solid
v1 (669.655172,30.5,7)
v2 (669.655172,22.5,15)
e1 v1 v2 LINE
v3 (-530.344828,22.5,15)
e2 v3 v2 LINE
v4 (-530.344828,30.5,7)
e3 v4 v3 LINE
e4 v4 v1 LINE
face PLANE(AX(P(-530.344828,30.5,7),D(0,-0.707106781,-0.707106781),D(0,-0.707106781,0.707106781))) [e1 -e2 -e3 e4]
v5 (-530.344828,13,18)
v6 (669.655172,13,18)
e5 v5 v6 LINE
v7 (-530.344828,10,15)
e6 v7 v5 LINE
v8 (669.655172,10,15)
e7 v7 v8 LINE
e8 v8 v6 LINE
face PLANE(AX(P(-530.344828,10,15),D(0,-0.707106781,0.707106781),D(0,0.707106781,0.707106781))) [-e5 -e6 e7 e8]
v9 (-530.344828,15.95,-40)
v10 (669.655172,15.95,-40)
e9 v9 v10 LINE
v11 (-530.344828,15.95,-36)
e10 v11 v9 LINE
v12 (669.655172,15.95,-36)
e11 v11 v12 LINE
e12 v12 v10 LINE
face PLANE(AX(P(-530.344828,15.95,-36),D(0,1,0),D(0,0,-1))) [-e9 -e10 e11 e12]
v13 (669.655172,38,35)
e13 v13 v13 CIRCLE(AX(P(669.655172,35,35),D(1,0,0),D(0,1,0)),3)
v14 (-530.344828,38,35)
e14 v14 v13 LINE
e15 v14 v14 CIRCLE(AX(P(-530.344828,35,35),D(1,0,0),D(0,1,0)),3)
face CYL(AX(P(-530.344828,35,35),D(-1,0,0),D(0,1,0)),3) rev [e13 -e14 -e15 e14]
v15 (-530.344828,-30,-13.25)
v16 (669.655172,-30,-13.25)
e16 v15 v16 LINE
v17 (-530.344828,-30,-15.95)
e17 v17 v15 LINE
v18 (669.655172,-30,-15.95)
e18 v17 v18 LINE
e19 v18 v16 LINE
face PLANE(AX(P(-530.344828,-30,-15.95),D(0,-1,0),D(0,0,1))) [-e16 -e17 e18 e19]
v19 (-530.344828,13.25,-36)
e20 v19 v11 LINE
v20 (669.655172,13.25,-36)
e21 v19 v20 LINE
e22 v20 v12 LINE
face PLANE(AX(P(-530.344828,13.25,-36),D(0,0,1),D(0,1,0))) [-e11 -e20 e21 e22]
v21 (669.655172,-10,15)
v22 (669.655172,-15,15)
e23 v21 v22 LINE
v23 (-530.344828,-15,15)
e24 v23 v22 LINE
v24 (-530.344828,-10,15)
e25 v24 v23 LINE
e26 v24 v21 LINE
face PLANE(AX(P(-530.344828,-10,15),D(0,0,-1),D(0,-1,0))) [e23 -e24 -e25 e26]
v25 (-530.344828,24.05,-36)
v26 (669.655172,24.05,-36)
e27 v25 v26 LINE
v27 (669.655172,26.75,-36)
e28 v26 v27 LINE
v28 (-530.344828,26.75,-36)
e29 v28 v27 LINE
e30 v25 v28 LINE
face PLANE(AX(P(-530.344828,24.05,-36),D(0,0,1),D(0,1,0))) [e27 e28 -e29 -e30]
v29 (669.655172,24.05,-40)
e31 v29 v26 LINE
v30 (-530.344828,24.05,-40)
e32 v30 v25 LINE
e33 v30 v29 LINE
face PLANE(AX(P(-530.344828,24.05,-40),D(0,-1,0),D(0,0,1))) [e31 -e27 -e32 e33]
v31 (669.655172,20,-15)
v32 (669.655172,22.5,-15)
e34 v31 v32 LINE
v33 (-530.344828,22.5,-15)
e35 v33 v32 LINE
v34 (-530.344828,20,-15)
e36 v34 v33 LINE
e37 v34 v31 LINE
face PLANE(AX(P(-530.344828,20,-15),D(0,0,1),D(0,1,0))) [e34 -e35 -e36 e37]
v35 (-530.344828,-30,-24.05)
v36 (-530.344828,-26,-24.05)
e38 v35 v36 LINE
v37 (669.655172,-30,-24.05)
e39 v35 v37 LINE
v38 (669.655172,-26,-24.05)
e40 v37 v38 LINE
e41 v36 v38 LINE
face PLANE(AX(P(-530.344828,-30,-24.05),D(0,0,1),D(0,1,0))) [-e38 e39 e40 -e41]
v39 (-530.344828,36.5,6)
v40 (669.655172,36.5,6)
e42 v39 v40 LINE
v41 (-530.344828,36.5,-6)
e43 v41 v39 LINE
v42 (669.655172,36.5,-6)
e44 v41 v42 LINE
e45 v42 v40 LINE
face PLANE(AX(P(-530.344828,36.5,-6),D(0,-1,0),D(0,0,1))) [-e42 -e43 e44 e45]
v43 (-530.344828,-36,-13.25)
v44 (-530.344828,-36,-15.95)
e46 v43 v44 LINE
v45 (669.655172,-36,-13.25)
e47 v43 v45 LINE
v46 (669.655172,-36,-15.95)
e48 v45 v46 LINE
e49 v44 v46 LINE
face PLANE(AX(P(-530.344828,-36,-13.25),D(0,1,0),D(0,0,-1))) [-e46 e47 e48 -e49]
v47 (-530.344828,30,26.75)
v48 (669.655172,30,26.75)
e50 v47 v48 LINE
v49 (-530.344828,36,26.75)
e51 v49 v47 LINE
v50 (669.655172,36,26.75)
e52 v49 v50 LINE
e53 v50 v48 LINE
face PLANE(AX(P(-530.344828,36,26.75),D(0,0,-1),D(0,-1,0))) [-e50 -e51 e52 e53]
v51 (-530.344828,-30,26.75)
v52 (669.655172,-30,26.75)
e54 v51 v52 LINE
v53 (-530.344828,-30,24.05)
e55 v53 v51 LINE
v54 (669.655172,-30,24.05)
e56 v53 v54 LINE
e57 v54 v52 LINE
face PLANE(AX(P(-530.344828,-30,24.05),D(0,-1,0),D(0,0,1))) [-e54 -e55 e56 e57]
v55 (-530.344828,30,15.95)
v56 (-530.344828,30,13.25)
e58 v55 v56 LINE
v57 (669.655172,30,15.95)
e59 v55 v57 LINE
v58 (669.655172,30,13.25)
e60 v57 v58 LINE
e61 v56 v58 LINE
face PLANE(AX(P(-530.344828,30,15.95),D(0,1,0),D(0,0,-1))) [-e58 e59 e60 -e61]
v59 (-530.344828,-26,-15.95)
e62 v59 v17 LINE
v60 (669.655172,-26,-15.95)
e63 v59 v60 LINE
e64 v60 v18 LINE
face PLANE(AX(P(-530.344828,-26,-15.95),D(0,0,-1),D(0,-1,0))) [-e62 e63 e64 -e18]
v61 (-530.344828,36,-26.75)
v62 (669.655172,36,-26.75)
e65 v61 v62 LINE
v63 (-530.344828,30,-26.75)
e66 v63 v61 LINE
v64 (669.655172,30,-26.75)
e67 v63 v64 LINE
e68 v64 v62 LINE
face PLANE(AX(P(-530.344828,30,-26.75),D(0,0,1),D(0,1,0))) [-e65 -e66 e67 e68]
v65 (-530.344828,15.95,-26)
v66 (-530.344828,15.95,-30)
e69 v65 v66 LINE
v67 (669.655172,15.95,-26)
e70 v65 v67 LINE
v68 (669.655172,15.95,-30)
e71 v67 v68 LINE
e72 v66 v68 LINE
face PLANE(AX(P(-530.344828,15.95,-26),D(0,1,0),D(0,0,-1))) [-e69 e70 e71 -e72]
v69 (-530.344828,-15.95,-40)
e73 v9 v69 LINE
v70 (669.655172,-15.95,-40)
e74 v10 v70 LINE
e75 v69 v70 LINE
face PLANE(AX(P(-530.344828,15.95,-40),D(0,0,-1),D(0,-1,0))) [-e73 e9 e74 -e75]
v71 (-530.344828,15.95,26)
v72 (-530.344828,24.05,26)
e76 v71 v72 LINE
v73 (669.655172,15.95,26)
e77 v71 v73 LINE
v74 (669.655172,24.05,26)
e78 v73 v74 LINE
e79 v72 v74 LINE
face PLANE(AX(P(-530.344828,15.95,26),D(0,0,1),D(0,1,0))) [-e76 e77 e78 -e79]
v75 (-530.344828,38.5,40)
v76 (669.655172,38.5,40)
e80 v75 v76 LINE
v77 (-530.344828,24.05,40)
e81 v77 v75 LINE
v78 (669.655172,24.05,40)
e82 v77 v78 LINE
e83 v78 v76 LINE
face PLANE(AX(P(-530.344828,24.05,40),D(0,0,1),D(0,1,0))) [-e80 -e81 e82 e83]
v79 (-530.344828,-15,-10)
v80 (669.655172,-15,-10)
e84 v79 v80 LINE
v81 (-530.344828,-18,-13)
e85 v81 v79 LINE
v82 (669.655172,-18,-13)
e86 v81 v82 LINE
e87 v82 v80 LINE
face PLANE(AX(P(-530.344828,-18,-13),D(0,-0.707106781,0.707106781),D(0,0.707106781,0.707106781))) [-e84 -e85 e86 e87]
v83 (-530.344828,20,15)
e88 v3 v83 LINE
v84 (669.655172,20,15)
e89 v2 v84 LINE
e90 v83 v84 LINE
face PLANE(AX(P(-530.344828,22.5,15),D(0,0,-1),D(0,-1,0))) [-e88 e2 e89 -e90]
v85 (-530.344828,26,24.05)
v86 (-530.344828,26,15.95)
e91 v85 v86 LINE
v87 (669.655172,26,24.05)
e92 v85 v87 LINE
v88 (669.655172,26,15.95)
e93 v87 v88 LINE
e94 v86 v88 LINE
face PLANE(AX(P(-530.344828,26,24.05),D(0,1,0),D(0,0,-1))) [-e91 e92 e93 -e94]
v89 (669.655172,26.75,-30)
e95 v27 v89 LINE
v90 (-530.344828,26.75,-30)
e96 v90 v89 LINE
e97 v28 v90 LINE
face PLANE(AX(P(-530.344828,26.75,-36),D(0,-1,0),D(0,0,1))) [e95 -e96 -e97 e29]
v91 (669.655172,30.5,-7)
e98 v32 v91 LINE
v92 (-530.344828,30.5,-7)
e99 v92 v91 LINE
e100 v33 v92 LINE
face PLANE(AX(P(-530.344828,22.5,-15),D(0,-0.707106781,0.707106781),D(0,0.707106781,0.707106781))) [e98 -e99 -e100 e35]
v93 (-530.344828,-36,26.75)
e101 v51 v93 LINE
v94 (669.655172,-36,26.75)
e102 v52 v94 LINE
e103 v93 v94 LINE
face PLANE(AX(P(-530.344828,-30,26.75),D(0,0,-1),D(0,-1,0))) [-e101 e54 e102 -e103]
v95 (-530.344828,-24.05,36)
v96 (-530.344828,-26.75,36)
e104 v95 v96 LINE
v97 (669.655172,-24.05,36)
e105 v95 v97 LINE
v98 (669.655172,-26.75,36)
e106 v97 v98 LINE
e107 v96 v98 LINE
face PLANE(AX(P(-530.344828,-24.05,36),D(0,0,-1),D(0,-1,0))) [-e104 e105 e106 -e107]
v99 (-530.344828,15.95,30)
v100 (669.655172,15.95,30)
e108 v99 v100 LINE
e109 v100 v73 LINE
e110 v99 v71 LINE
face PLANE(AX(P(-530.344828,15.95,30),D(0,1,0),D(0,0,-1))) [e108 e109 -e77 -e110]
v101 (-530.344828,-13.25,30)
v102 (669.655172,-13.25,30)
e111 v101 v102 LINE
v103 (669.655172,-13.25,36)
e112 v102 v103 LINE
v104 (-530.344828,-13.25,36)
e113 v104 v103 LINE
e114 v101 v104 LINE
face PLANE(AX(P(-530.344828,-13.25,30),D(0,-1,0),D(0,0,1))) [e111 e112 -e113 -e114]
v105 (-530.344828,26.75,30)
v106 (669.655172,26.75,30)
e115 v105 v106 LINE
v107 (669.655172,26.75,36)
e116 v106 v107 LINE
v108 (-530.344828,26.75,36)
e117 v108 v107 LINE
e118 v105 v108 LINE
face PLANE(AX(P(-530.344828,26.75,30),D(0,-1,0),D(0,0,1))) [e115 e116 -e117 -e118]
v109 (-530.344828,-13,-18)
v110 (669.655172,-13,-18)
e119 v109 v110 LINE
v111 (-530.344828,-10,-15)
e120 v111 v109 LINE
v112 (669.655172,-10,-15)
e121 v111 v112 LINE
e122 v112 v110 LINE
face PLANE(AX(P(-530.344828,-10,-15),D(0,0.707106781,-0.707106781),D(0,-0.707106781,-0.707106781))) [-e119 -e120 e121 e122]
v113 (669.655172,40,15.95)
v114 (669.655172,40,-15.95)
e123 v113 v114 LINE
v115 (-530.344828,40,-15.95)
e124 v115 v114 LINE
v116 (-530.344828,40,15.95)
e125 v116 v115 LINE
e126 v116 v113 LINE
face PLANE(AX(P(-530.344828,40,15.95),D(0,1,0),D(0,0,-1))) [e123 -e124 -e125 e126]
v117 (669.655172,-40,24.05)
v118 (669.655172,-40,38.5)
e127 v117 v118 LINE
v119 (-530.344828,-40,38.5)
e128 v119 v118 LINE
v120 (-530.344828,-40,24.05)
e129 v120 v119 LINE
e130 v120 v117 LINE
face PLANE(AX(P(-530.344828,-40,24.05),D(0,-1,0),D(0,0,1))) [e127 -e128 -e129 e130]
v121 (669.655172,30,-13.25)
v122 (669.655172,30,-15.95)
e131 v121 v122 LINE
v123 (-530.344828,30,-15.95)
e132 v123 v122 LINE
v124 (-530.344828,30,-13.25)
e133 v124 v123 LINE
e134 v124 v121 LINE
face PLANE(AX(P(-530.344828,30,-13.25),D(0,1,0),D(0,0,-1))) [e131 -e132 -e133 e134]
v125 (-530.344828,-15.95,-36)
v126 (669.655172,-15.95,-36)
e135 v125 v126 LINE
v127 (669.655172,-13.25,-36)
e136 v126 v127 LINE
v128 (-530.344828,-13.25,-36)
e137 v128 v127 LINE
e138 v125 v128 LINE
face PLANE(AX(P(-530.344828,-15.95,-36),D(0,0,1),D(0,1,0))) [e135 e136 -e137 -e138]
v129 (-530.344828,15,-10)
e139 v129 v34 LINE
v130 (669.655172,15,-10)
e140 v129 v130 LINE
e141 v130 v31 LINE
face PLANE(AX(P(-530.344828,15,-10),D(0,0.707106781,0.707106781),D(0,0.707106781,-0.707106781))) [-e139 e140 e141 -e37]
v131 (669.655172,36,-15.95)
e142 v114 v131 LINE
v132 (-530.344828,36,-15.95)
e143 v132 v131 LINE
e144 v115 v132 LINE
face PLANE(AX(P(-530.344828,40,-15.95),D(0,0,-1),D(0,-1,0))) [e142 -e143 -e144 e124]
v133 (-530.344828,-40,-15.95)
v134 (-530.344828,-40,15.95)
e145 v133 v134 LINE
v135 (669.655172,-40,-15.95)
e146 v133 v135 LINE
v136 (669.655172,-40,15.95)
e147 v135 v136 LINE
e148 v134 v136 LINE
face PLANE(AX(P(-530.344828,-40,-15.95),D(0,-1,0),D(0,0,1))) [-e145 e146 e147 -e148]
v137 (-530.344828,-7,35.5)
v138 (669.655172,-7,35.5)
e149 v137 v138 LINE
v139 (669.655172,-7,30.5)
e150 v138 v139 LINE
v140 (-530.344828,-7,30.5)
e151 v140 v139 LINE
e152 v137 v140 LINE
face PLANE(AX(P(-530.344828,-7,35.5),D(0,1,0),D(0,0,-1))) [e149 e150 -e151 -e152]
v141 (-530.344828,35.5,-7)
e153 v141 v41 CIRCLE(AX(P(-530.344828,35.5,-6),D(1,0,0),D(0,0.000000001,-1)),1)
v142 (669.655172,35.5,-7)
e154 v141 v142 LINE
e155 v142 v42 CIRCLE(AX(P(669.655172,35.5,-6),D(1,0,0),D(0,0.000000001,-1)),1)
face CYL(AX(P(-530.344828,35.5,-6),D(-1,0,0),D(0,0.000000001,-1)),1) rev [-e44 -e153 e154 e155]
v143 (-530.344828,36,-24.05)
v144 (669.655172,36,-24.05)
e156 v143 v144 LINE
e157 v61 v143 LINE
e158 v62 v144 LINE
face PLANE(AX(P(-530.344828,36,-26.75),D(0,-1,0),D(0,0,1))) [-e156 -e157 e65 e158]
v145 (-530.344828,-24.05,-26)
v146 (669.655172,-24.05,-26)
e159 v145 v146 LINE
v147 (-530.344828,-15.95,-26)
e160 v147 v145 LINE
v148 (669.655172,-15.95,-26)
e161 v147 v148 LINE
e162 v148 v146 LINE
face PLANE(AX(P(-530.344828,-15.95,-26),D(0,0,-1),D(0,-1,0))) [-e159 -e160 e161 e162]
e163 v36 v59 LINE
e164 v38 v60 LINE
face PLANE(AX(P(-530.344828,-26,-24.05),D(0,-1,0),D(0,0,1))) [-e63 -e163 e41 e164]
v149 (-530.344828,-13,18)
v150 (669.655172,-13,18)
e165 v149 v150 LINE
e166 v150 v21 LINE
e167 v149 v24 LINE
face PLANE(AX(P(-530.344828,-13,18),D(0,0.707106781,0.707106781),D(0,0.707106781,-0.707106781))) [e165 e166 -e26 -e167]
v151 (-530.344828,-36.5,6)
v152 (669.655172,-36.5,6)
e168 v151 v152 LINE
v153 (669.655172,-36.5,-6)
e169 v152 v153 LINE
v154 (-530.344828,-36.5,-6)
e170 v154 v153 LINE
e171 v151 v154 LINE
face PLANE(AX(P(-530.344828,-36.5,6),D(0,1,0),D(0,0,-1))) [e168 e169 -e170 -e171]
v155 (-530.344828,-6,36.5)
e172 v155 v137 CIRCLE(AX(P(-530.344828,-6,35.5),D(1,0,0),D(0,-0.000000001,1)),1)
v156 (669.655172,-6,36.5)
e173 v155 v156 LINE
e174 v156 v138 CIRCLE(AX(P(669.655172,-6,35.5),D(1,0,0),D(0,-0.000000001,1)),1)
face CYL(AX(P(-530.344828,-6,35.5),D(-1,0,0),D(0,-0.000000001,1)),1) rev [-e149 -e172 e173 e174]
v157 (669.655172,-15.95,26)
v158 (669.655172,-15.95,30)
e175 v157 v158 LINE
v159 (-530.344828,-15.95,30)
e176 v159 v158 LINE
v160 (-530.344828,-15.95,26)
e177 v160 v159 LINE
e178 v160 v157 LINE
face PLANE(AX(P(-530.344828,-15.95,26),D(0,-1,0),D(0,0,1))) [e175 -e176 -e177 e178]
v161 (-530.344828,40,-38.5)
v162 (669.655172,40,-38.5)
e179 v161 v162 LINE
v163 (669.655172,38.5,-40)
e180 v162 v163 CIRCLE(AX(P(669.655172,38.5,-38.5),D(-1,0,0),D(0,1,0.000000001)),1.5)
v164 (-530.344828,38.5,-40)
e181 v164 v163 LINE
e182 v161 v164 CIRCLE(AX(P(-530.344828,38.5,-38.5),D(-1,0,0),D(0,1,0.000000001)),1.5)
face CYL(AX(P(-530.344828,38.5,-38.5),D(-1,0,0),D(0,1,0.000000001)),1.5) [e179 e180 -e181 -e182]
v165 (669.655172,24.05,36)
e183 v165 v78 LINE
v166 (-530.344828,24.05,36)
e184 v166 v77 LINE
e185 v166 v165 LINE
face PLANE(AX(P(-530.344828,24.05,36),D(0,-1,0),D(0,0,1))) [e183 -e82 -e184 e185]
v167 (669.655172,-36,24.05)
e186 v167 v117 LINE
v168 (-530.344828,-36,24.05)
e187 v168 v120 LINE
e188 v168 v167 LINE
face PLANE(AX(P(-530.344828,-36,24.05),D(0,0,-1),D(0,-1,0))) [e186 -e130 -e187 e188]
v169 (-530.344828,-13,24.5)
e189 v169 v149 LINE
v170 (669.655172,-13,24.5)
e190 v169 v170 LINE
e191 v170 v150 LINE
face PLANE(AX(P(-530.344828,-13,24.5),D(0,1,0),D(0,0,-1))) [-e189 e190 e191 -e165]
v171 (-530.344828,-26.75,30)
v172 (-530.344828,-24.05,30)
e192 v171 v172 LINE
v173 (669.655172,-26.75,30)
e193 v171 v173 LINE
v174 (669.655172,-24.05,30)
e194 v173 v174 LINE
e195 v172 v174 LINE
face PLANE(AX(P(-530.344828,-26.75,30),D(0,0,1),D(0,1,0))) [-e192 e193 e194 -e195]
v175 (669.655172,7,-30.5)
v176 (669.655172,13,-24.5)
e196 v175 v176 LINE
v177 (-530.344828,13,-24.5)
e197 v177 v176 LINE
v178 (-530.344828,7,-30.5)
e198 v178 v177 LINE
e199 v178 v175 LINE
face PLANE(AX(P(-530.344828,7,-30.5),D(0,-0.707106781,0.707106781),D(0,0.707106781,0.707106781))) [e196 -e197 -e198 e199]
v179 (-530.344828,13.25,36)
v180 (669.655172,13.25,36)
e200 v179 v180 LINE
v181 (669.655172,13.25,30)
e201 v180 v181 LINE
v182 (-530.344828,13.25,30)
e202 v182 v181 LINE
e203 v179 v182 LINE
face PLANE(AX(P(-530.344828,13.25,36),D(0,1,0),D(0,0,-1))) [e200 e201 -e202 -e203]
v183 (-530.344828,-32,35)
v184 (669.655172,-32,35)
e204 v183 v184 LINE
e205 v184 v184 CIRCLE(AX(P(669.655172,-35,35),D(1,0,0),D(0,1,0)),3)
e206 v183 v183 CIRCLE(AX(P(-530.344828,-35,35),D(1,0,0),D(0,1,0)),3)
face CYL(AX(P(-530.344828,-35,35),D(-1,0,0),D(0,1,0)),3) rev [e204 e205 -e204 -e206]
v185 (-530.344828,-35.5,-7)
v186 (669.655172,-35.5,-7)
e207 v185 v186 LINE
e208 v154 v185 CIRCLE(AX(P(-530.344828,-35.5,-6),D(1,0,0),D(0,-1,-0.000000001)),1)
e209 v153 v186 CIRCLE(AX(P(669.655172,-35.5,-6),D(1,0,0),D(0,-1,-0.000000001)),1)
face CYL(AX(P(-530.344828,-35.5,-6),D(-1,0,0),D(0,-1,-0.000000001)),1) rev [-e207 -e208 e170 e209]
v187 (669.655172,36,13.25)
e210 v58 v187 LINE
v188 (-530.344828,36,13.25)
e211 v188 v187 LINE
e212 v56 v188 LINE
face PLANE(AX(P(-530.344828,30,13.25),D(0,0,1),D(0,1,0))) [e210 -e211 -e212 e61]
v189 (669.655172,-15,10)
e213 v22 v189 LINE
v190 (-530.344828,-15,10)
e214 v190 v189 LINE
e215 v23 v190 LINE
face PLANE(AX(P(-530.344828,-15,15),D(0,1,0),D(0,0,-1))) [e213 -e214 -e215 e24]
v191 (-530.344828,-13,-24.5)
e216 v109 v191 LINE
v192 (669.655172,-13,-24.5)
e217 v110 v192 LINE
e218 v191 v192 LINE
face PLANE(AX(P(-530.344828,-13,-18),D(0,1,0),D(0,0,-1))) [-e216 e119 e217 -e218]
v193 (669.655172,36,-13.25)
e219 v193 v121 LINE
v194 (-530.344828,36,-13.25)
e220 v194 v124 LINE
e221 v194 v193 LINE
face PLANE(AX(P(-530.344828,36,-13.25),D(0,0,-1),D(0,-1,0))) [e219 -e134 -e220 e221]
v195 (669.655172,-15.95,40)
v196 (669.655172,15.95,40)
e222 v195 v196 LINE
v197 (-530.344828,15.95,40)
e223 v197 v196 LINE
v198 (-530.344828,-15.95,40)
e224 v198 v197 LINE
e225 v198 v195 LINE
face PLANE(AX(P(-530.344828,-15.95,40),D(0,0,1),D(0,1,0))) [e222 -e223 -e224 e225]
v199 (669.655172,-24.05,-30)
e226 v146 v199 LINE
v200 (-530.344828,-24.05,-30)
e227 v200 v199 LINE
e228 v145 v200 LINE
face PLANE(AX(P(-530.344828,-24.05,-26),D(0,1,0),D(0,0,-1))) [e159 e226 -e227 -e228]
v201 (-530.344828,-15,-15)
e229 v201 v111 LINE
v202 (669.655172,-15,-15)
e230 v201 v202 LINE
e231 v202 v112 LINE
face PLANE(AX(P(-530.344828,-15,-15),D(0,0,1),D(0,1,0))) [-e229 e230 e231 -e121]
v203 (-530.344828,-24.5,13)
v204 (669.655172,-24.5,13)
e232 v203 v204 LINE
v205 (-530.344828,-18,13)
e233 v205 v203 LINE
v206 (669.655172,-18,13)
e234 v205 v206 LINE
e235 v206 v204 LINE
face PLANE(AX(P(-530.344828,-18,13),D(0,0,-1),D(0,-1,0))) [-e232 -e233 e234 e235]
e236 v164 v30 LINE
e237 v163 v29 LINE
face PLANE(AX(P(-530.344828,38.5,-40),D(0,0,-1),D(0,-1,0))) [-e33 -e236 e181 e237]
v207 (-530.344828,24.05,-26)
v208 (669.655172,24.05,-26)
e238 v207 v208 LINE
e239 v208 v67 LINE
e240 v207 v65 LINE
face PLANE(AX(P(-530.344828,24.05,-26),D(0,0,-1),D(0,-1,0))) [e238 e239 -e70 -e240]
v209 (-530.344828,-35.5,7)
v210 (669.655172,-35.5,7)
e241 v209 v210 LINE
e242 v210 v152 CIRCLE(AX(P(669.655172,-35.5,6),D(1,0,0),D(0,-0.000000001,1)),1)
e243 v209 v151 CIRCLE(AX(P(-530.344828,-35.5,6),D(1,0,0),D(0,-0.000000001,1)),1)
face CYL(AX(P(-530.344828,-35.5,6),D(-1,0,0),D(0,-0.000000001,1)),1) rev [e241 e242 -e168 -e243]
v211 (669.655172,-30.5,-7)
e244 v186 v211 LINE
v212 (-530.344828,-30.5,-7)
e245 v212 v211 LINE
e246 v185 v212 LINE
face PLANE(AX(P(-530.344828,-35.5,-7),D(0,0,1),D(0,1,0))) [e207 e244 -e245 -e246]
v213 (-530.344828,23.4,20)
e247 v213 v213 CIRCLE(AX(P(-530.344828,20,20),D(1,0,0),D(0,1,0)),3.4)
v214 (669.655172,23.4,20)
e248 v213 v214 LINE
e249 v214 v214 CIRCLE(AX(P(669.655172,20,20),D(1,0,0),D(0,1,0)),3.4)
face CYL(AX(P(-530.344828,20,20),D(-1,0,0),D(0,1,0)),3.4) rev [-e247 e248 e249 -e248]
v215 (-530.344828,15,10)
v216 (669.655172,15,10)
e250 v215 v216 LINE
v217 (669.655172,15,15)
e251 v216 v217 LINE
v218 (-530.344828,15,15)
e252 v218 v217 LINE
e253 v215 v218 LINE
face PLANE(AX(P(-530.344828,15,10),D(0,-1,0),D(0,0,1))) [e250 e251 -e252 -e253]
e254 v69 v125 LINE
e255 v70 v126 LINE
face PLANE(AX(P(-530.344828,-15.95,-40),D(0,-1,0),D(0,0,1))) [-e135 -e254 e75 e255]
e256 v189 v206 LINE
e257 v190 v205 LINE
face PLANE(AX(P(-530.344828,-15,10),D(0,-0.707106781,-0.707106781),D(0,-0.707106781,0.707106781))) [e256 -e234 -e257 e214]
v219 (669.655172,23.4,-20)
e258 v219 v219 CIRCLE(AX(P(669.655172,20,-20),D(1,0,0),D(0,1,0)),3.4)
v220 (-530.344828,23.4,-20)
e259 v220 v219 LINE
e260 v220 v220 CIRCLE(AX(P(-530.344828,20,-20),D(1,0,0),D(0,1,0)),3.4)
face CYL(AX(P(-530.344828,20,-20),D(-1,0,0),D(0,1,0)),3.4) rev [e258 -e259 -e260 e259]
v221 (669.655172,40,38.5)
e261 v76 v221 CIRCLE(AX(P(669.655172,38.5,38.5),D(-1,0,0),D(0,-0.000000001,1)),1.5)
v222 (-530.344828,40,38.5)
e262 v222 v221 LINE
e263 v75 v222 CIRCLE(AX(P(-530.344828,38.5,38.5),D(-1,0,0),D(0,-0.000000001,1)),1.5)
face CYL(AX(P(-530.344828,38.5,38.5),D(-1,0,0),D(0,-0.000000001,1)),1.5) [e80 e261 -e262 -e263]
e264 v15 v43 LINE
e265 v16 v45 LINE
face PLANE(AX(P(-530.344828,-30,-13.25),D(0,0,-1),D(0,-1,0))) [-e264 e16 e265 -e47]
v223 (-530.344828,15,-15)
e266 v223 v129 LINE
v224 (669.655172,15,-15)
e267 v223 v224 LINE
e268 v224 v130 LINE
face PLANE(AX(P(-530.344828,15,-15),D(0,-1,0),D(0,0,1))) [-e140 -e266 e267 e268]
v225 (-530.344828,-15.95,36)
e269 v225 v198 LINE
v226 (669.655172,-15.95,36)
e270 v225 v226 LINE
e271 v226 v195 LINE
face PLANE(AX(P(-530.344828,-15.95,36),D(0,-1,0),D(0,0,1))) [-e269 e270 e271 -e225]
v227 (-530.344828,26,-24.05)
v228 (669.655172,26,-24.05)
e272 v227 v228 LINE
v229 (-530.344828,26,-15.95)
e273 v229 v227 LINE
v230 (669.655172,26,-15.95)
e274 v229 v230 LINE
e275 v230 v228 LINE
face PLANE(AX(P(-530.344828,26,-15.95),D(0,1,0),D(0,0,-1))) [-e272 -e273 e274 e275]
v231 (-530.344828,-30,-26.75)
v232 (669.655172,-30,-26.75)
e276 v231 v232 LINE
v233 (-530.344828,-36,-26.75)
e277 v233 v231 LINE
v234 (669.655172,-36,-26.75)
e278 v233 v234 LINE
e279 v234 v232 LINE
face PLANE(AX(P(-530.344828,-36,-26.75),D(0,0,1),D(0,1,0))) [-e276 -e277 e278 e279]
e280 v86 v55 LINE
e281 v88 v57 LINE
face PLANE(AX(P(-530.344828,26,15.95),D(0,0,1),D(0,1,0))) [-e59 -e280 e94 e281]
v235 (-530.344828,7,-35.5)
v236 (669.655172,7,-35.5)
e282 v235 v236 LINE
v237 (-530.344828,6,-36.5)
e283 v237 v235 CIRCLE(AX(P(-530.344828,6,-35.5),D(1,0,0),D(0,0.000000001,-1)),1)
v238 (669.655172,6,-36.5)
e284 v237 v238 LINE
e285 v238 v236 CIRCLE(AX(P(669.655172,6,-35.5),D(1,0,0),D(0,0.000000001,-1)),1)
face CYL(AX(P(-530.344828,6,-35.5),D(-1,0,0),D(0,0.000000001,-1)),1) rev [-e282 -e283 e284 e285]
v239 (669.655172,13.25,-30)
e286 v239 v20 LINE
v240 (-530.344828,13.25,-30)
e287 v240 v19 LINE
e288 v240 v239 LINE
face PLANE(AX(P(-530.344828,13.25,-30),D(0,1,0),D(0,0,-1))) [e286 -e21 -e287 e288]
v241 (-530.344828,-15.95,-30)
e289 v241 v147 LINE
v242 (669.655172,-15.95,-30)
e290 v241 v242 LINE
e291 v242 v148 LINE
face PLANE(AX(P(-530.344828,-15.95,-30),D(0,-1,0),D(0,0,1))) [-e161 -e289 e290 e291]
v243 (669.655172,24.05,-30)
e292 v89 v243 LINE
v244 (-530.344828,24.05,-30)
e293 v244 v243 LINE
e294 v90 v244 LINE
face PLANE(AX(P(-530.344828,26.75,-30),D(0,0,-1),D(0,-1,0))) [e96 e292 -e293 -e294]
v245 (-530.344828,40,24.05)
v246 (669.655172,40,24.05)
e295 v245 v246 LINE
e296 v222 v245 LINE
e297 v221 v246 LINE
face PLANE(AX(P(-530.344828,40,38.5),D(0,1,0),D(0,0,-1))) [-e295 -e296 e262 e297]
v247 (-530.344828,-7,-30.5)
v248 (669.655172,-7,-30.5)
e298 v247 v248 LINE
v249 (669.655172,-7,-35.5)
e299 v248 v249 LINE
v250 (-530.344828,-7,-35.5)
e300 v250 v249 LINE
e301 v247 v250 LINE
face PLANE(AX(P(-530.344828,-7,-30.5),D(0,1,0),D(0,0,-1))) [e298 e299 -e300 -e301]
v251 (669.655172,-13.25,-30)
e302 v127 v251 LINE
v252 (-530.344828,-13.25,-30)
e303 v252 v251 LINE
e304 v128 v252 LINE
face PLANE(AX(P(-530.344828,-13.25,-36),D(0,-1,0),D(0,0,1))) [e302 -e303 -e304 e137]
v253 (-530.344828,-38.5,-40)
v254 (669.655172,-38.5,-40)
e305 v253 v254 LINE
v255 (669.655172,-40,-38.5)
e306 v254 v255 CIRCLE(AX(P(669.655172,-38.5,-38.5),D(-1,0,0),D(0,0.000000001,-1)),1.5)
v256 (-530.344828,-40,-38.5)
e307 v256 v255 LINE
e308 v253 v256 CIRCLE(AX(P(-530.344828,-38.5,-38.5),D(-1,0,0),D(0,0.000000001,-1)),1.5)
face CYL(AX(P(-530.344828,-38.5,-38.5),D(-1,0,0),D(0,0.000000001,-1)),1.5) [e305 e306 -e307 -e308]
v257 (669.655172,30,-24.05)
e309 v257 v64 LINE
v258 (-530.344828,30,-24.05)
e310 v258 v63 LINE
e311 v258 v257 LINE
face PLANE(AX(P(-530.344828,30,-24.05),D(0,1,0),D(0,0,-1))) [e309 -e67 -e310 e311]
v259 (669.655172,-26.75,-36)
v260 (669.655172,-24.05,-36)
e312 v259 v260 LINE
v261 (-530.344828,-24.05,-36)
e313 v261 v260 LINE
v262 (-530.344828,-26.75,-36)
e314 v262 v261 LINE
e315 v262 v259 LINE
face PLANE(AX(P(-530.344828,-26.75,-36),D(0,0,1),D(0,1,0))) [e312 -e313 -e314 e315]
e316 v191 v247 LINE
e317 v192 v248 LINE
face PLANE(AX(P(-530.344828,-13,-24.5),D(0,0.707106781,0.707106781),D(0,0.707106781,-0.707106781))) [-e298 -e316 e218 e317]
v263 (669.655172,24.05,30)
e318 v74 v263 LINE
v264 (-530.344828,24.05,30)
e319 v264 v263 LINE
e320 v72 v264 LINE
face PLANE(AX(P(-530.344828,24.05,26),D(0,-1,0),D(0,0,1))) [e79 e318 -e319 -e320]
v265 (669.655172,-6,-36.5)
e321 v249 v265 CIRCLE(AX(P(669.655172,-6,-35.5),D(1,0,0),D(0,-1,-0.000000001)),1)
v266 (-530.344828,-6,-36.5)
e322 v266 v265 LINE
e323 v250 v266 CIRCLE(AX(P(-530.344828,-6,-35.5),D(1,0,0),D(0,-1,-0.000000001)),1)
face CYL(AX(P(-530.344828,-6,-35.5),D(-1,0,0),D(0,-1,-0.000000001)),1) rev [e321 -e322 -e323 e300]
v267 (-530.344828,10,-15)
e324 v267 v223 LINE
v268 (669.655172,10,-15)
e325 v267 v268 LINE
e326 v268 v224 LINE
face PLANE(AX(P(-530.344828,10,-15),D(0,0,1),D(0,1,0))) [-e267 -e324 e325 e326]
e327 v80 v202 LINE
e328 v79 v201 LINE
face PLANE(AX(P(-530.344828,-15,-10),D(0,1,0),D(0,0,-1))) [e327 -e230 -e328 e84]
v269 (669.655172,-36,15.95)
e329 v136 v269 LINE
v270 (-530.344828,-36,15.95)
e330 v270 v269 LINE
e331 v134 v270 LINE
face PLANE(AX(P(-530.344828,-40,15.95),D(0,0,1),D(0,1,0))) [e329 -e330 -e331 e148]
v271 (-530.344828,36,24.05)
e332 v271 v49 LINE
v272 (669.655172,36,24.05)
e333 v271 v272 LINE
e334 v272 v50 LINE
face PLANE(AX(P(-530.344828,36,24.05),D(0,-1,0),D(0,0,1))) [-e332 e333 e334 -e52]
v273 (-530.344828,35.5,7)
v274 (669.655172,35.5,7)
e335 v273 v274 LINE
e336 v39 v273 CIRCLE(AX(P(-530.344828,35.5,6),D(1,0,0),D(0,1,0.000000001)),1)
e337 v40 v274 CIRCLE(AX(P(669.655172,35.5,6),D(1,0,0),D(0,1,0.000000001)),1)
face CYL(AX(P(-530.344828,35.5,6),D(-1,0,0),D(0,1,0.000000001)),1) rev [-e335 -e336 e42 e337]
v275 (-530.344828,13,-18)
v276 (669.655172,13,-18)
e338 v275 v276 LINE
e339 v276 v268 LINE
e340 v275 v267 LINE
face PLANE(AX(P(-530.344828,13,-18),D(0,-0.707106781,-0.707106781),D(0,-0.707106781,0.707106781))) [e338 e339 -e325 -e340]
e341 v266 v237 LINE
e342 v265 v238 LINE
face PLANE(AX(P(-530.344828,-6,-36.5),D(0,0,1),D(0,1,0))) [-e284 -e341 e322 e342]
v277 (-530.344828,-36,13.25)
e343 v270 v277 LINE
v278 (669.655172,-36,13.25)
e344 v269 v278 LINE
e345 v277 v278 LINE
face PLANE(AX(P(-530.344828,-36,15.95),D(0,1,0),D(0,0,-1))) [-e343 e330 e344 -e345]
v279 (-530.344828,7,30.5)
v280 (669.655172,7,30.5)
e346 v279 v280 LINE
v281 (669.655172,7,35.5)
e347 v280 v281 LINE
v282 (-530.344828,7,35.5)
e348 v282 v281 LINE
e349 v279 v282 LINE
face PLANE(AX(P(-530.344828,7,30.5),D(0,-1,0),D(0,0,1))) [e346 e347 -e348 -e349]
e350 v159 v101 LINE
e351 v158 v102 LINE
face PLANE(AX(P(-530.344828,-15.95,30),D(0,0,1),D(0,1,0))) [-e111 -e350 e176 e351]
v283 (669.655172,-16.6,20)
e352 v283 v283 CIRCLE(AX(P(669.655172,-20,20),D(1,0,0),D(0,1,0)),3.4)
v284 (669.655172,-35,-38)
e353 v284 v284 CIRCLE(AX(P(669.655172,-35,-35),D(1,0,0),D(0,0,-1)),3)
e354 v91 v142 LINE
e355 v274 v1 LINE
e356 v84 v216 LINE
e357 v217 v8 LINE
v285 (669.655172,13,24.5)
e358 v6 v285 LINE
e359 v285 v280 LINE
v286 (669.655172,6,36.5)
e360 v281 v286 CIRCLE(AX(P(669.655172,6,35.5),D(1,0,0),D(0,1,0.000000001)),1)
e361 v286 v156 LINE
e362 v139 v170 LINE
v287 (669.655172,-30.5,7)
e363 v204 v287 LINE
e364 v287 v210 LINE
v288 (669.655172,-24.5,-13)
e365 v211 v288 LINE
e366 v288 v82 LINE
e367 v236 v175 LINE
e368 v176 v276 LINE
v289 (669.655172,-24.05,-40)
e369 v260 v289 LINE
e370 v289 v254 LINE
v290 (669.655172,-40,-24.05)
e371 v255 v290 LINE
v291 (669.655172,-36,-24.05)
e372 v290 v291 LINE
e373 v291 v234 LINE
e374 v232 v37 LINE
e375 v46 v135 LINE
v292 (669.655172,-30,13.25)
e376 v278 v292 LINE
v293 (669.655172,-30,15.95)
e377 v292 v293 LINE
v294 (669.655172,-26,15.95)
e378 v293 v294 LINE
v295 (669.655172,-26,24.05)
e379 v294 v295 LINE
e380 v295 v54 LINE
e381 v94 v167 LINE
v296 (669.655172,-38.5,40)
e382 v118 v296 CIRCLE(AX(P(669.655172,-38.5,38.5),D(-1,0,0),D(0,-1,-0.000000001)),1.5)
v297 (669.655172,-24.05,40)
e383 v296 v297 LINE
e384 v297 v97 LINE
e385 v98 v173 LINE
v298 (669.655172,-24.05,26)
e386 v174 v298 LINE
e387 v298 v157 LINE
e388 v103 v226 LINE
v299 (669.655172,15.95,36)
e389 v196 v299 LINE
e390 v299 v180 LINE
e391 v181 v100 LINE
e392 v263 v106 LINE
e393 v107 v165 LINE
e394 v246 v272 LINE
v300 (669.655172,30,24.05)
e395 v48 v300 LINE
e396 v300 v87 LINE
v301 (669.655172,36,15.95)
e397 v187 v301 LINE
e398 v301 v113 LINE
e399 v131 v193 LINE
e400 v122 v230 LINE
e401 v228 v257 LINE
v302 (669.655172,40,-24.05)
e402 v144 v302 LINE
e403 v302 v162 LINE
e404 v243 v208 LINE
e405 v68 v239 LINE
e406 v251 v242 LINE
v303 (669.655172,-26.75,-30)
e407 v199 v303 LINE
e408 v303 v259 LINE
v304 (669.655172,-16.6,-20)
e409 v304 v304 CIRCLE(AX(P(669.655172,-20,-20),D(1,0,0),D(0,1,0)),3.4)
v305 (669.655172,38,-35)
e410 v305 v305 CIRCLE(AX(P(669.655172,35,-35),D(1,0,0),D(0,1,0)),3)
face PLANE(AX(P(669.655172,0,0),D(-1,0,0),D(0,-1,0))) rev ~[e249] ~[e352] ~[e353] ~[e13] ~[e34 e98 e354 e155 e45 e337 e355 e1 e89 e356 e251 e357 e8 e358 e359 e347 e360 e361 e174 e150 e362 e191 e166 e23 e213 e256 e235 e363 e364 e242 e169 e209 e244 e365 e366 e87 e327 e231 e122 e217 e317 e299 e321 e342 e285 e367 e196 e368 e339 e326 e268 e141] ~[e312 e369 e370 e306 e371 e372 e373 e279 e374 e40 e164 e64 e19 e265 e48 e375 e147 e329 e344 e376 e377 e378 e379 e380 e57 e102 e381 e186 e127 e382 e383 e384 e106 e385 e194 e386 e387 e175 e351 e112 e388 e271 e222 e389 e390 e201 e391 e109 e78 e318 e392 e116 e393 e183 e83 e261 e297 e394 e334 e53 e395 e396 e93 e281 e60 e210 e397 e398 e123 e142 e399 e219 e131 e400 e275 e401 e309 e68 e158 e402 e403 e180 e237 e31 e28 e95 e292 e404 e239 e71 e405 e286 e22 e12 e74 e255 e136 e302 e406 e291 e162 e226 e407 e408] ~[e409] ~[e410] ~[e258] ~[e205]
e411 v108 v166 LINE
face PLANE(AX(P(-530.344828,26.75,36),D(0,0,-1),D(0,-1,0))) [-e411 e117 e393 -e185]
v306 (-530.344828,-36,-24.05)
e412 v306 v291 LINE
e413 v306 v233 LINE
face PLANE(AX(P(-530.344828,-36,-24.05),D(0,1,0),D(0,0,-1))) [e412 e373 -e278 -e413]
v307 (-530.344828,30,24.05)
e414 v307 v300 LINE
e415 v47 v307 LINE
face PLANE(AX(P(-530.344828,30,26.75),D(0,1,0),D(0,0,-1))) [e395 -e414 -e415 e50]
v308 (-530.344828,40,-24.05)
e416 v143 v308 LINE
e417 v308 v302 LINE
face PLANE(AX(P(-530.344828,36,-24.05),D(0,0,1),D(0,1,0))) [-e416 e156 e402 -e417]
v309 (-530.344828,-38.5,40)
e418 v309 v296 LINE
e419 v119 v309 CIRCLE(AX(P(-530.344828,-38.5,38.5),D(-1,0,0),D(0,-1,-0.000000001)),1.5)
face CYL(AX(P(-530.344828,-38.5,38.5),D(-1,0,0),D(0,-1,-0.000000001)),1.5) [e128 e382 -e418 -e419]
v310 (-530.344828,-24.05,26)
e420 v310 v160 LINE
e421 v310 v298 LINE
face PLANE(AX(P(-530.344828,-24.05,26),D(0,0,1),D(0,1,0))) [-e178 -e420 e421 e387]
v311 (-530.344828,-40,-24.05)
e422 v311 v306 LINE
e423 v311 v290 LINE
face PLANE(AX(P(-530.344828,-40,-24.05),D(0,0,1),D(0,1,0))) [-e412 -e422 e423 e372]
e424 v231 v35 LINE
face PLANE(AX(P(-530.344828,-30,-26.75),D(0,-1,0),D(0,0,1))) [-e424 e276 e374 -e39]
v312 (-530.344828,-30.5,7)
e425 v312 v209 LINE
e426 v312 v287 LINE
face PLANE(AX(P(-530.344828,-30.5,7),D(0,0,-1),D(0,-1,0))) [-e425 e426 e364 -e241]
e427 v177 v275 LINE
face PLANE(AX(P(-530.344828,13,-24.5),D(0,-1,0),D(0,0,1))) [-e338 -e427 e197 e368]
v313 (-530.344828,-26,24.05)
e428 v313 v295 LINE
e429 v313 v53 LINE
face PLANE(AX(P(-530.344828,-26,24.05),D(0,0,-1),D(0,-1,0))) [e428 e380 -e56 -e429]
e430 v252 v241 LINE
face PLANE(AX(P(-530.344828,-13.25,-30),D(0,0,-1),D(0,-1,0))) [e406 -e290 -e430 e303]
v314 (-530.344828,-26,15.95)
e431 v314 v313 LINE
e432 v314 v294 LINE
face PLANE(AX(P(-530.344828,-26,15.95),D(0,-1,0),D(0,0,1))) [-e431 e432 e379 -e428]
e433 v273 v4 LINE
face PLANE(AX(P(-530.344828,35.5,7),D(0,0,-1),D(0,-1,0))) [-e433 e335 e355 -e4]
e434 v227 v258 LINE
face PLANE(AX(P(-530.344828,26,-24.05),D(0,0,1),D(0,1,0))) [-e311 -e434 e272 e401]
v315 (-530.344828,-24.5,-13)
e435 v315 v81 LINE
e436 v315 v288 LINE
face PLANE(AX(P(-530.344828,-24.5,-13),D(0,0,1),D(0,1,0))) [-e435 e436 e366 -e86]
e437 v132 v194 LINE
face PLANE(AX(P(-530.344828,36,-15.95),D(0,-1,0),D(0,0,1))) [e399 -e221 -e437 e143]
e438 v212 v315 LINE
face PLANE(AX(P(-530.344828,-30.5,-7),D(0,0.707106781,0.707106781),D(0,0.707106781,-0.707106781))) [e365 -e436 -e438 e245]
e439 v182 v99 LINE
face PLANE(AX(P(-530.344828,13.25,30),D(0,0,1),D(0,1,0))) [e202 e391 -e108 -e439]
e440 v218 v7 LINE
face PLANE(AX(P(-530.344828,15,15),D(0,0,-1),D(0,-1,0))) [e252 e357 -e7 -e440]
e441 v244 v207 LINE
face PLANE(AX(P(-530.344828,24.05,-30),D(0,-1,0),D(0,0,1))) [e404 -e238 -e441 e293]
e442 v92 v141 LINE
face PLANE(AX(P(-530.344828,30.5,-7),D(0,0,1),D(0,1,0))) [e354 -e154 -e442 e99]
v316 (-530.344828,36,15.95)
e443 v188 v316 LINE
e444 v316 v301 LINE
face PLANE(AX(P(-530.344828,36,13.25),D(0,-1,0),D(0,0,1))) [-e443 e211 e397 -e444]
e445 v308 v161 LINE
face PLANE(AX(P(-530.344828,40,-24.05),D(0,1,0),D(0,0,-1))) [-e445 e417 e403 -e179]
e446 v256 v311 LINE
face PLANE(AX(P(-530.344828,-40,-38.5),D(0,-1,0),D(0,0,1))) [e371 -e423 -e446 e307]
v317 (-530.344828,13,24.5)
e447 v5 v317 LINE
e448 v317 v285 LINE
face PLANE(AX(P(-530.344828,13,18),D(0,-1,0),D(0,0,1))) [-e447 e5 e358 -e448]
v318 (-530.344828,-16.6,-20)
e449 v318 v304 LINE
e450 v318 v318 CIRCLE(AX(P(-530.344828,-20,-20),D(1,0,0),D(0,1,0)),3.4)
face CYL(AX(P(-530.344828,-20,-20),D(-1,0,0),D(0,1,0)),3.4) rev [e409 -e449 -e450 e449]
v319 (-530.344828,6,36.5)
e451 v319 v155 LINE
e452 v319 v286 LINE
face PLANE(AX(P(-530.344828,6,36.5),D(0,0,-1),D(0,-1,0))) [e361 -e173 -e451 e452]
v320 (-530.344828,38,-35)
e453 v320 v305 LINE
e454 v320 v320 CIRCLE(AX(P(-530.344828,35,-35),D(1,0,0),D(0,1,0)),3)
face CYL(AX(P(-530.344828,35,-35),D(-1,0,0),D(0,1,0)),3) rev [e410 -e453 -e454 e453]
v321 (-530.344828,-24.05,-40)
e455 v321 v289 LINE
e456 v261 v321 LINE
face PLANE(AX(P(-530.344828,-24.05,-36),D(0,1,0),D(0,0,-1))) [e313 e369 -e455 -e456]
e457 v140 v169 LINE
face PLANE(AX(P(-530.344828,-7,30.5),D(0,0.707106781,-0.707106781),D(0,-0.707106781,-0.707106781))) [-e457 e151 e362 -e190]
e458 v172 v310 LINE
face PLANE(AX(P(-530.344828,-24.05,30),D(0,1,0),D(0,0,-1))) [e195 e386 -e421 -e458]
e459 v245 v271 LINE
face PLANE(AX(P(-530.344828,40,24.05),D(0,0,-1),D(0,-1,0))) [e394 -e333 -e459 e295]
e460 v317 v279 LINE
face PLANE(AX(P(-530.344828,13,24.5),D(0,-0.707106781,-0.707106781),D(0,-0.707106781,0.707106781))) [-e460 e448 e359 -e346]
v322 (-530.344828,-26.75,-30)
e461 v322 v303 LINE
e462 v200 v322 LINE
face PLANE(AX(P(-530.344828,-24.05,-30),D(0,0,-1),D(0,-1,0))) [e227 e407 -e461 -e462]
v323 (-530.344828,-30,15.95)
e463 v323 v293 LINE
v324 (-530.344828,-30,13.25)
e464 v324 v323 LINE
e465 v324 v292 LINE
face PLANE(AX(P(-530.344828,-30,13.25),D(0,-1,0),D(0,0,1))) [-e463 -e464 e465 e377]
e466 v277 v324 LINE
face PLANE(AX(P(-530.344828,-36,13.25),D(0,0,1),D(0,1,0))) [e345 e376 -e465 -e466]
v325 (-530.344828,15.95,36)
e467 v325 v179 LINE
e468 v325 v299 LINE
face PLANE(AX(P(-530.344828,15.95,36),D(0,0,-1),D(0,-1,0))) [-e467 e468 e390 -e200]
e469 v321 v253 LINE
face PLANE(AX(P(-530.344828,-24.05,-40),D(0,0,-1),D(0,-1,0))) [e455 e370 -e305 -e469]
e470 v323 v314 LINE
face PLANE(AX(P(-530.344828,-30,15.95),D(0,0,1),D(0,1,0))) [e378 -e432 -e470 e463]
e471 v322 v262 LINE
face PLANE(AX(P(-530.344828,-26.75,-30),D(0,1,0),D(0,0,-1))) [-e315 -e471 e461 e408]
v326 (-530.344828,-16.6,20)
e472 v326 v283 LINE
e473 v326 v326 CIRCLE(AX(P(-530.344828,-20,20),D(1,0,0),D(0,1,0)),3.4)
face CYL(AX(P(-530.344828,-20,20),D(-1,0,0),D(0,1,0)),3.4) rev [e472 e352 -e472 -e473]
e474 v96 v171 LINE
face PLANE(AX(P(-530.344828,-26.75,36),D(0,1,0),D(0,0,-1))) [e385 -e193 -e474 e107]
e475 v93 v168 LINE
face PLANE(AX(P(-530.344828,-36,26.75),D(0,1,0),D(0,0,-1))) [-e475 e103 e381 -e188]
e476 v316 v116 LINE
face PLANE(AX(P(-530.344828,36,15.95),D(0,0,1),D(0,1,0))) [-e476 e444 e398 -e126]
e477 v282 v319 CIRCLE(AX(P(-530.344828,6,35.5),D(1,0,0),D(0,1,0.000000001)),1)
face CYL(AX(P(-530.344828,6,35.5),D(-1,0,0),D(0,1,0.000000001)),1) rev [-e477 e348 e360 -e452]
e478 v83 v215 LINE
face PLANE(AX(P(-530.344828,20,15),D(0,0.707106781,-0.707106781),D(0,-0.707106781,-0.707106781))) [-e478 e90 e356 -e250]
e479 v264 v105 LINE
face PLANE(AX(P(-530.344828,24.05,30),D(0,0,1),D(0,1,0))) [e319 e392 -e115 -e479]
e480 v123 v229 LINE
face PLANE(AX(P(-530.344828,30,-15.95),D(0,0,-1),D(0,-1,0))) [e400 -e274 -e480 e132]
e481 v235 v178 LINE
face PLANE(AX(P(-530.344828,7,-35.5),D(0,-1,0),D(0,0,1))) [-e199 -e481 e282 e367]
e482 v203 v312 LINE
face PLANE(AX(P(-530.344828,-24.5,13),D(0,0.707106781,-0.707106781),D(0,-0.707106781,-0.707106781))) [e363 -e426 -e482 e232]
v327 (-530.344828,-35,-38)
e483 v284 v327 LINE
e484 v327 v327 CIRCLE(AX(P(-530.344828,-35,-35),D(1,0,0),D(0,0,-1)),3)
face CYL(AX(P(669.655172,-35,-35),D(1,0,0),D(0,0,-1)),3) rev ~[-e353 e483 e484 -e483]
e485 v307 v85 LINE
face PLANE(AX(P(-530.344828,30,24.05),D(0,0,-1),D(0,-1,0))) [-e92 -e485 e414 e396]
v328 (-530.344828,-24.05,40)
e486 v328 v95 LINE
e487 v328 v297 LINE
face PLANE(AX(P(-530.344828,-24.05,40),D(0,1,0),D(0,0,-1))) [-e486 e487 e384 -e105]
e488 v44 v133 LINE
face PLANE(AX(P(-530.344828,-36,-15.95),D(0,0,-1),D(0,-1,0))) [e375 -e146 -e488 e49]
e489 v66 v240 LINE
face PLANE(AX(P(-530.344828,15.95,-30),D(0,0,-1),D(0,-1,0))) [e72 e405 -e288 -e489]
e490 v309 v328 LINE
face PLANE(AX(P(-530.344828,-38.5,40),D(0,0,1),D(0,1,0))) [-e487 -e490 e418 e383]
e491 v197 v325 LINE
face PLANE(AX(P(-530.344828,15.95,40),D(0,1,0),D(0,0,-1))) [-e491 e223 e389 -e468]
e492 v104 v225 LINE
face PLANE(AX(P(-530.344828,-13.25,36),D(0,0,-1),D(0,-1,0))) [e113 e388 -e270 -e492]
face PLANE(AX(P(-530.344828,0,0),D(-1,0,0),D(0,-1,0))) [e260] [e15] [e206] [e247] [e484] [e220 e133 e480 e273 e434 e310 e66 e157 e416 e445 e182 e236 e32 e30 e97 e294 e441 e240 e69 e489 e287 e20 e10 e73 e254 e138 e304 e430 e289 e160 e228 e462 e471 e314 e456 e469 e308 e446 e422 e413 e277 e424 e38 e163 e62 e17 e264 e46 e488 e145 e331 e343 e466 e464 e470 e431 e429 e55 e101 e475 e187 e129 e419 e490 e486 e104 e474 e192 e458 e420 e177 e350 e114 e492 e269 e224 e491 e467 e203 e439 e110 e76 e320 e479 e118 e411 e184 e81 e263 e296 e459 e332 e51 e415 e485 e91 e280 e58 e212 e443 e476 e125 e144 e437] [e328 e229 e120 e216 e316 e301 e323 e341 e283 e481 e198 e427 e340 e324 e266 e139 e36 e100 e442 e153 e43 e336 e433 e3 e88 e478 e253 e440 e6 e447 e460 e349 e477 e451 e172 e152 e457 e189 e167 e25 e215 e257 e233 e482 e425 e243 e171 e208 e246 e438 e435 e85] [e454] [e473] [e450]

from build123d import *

# Parameters (mm, degrees)
SKETCH1_R                                = 3.4
SKETCH1_R_2                              = 3
ALUMINUM_PROFILE_80_X_80G_X_R1_5_1_DEPTH = 1200
SKETCH10_R                               = 3
CUT_EXTRUDE1_DEPTH                       = 1202.332593414


with BuildPart() as part:
    # Sketch1 → Aluminum profile 80 X 80G X R1.5(1) (new body)
    with BuildSketch(Plane.YZ.offset(-530.344827586)):
        with BuildLine():
            Line((-24.05, 40), (-24.05, 36))
            Line((-24.05, 36), (-26.75, 36))
            Line((-26.75, 36), (-26.75, 30))
            Line((-26.75, 30), (-24.05, 30))
            Line((-24.05, 30), (-24.05, 26))
            Line((-24.05, 26), (-15.95, 26))
            Line((-15.95, 26), (-15.95, 30))
            Line((-15.95, 30), (-13.25, 30))
            Line((-13.25, 30), (-13.25, 36))
            Line((-13.25, 36), (-15.95, 36))
            Line((-15.95, 36), (-15.95, 40))
            Line((-15.95, 40), (15.95, 40))
            Line((15.95, 40), (15.95, 36))
            Line((15.95, 36), (13.25, 36))
            Line((13.25, 36), (13.25, 30))
            Line((13.25, 30), (15.95, 30))
            Line((15.95, 30), (15.95, 26))
            Line((15.95, 26), (24.05, 26))
            Line((24.05, 26), (24.05, 30))
            Line((24.05, 30), (26.75, 30))
            Line((26.75, 30), (26.75, 36))
            Line((26.75, 36), (24.05, 36))
            Line((24.05, 36), (24.05, 40))
            Line((24.05, 40), (38.5, 40))
            ThreePointArc((38.5, 40), (39.560660172, 39.560660172), (40, 38.5))
            Line((40, 38.5), (40, 24.05))
            Line((40, 24.05), (36, 24.05))
            Line((36, 24.05), (36, 26.75))
            Line((36, 26.75), (30, 26.75))
            Line((30, 26.75), (30, 24.05))
            Line((30, 24.05), (26, 24.05))
            Line((26, 24.05), (26, 15.95))
            Line((26, 15.95), (30, 15.95))
            Line((30, 15.95), (30, 13.25))
            Line((30, 13.25), (36, 13.25))
            Line((36, 13.25), (36, 15.95))
            Line((36, 15.95), (40, 15.95))
            Line((40, 15.95), (40, -15.95))
            Line((40, -15.95), (36, -15.95))
            Line((36, -15.95), (36, -13.25))
            Line((36, -13.25), (30, -13.25))
            Line((30, -13.25), (30, -15.95))
            Line((30, -15.95), (26, -15.95))
            Line((26, -15.95), (26, -24.05))
            Line((26, -24.05), (30, -24.05))
            Line((30, -24.05), (30, -26.75))
            Line((30, -26.75), (36, -26.75))
            Line((36, -26.75), (36, -24.05))
            Line((36, -24.05), (40, -24.05))
            Line((40, -24.05), (40, -38.5))
            ThreePointArc((40, -38.5), (39.560660172, -39.560660172), (38.5, -40))
            Line((38.5, -40), (24.05, -40))
            Line((24.05, -40), (24.05, -36))
            Line((24.05, -36), (26.75, -36))
            Line((26.75, -36), (26.75, -30))
            Line((26.75, -30), (24.05, -30))
            Line((24.05, -30), (24.05, -26))
            Line((24.05, -26), (15.95, -26))
            Line((15.95, -26), (15.95, -30))
            Line((15.95, -30), (13.25, -30))
            Line((13.25, -30), (13.25, -36))
            Line((13.25, -36), (15.95, -36))
            Line((15.95, -36), (15.95, -40))
            Line((15.95, -40), (-15.95, -40))
            Line((-15.95, -40), (-15.95, -36))
            Line((-15.95, -36), (-13.25, -36))
            Line((-13.25, -36), (-13.25, -30))
            Line((-13.25, -30), (-15.95, -30))
            Line((-15.95, -30), (-15.95, -26))
            Line((-15.95, -26), (-24.05, -26))
            Line((-24.05, -26), (-24.05, -30))
            Line((-24.05, -30), (-26.75, -30))
            Line((-26.75, -30), (-26.75, -36))
            Line((-26.75, -36), (-24.05, -36))
            Line((-24.05, -36), (-24.05, -40))
            Line((-24.05, -40), (-38.5, -40))
            ThreePointArc((-38.5, -40), (-39.560660172, -39.560660172), (-40, -38.5))
            Line((-40, -38.5), (-40, -24.05))
            Line((-40, -24.05), (-36, -24.05))
            Line((-36, -24.05), (-36, -26.75))
            Line((-36, -26.75), (-30, -26.75))
            Line((-30, -26.75), (-30, -24.05))
            Line((-30, -24.05), (-26, -24.05))
            Line((-26, -24.05), (-26, -15.95))
            Line((-26, -15.95), (-30, -15.95))
            Line((-30, -15.95), (-30, -13.25))
            Line((-30, -13.25), (-36, -13.25))
            Line((-36, -13.25), (-36, -15.95))
            Line((-36, -15.95), (-40, -15.95))
            Line((-40, -15.95), (-40, 15.95))
            Line((-40, 15.95), (-36, 15.95))
            Line((-36, 15.95), (-36, 13.25))
            Line((-36, 13.25), (-30, 13.25))
            Line((-30, 13.25), (-30, 15.95))
            Line((-30, 15.95), (-26, 15.95))
            Line((-26, 15.95), (-26, 24.05))
            Line((-26, 24.05), (-30, 24.05))
            Line((-30, 24.05), (-30, 26.75))
            Line((-30, 26.75), (-36, 26.75))
            Line((-36, 26.75), (-36, 24.05))
            Line((-36, 24.05), (-40, 24.05))
            Line((-40, 24.05), (-40, 38.5))
            ThreePointArc((-40, 38.5), (-39.560660172, 39.560660172), (-38.5, 40))
            Line((-38.5, 40), (-24.05, 40))
        make_face()
        with Locations((-20, 20)):
            Circle(SKETCH1_R, mode=Mode.SUBTRACT)
        with Locations((20, 20)):
            Circle(SKETCH1_R, mode=Mode.SUBTRACT)
        with Locations((20, -20)):
            Circle(SKETCH1_R, mode=Mode.SUBTRACT)
        with Locations((-20, -20)):
            Circle(SKETCH1_R, mode=Mode.SUBTRACT)
        with Locations((-35, 35)):
            Circle(SKETCH1_R_2, mode=Mode.SUBTRACT)
        with Locations((35, 35)):
            Circle(SKETCH1_R_2, mode=Mode.SUBTRACT)
        with Locations((35, -35)):
            Circle(SKETCH1_R_2, mode=Mode.SUBTRACT)
        with BuildLine():
            Line((-13, 18), (-10, 15))
            Line((-10, 15), (-15, 15))
            Line((-15, 15), (-15, 10))
            Line((-15, 10), (-18, 13))
            Line((-18, 13), (-24.5, 13))
            Line((-24.5, 13), (-30.5, 7))
            Line((-30.5, 7), (-35.5, 7))
            ThreePointArc((-35.5, 7), (-36.207106781, 6.707106781), (-36.5, 6))
            Line((-36.5, 6), (-36.5, -6))
            ThreePointArc((-36.5, -6), (-36.207106781, -6.707106781), (-35.5, -7))
            Line((-35.5, -7), (-30.5, -7))
            Line((-30.5, -7), (-24.5, -13))
            Line((-24.5, -13), (-18, -13))
            Line((-18, -13), (-15, -10))
            Line((-15, -10), (-15, -15))
            Line((-15, -15), (-10, -15))
            Line((-10, -15), (-13, -18))
            Line((-13, -18), (-13, -24.5))
            Line((-13, -24.5), (-7, -30.5))
            Line((-7, -30.5), (-7, -35.5))
            ThreePointArc((-7, -35.5), (-6.707106781, -36.207106781), (-6, -36.5))
            Line((-6, -36.5), (6, -36.5))
            ThreePointArc((6, -36.5), (6.707106781, -36.207106781), (7, -35.5))
            Line((7, -35.5), (7, -30.5))
            Line((7, -30.5), (13, -24.5))
            Line((13, -24.5), (13, -18))
            Line((13, -18), (10, -15))
            Line((10, -15), (15, -15))
            Line((15, -15), (15, -10))
            Line((15, -10), (20, -15))
            Line((20, -15), (22.5, -15))
            Line((22.5, -15), (30.5, -7))
            Line((30.5, -7), (35.5, -7))
            ThreePointArc((35.5, -7), (36.207106781, -6.707106781), (36.5, -6))
            Line((36.5, -6), (36.5, 6))
            ThreePointArc((36.5, 6), (36.207106781, 6.707106781), (35.5, 7))
            Line((35.5, 7), (30.5, 7))
            Line((30.5, 7), (22.5, 15))
            Line((22.5, 15), (20, 15))
            Line((20, 15), (15, 10))
            Line((15, 10), (15, 15))
            Line((15, 15), (10, 15))
            Line((10, 15), (13, 18))
            Line((13, 18), (13, 24.5))
            Line((13, 24.5), (7, 30.5))
            Line((7, 30.5), (7, 35.5))
            ThreePointArc((7, 35.5), (6.707106781, 36.207106781), (6, 36.5))
            Line((6, 36.5), (-6, 36.5))
            ThreePointArc((-6, 36.5), (-6.707106781, 36.207106781), (-7, 35.5))
            Line((-7, 35.5), (-7, 30.5))
            Line((-7, 30.5), (-13, 24.5))
            Line((-13, 24.5), (-13, 18))
        make_face(mode=Mode.SUBTRACT)
    extrude(amount=ALUMINUM_PROFILE_80_X_80G_X_R1_5_1_DEPTH)

    # Sketch10 → Cut-Extrude1 (cut, through all)
    with BuildSketch(Plane(origin=(669.655172414, 0, 0), x_dir=(0, 0, -1), z_dir=(1, 0, 0))):
        with Locations((35, -35)):
            Circle(SKETCH10_R)
    extrude(amount=-CUT_EXTRUDE1_DEPTH, mode=Mode.SUBTRACT)


solid = part.part
